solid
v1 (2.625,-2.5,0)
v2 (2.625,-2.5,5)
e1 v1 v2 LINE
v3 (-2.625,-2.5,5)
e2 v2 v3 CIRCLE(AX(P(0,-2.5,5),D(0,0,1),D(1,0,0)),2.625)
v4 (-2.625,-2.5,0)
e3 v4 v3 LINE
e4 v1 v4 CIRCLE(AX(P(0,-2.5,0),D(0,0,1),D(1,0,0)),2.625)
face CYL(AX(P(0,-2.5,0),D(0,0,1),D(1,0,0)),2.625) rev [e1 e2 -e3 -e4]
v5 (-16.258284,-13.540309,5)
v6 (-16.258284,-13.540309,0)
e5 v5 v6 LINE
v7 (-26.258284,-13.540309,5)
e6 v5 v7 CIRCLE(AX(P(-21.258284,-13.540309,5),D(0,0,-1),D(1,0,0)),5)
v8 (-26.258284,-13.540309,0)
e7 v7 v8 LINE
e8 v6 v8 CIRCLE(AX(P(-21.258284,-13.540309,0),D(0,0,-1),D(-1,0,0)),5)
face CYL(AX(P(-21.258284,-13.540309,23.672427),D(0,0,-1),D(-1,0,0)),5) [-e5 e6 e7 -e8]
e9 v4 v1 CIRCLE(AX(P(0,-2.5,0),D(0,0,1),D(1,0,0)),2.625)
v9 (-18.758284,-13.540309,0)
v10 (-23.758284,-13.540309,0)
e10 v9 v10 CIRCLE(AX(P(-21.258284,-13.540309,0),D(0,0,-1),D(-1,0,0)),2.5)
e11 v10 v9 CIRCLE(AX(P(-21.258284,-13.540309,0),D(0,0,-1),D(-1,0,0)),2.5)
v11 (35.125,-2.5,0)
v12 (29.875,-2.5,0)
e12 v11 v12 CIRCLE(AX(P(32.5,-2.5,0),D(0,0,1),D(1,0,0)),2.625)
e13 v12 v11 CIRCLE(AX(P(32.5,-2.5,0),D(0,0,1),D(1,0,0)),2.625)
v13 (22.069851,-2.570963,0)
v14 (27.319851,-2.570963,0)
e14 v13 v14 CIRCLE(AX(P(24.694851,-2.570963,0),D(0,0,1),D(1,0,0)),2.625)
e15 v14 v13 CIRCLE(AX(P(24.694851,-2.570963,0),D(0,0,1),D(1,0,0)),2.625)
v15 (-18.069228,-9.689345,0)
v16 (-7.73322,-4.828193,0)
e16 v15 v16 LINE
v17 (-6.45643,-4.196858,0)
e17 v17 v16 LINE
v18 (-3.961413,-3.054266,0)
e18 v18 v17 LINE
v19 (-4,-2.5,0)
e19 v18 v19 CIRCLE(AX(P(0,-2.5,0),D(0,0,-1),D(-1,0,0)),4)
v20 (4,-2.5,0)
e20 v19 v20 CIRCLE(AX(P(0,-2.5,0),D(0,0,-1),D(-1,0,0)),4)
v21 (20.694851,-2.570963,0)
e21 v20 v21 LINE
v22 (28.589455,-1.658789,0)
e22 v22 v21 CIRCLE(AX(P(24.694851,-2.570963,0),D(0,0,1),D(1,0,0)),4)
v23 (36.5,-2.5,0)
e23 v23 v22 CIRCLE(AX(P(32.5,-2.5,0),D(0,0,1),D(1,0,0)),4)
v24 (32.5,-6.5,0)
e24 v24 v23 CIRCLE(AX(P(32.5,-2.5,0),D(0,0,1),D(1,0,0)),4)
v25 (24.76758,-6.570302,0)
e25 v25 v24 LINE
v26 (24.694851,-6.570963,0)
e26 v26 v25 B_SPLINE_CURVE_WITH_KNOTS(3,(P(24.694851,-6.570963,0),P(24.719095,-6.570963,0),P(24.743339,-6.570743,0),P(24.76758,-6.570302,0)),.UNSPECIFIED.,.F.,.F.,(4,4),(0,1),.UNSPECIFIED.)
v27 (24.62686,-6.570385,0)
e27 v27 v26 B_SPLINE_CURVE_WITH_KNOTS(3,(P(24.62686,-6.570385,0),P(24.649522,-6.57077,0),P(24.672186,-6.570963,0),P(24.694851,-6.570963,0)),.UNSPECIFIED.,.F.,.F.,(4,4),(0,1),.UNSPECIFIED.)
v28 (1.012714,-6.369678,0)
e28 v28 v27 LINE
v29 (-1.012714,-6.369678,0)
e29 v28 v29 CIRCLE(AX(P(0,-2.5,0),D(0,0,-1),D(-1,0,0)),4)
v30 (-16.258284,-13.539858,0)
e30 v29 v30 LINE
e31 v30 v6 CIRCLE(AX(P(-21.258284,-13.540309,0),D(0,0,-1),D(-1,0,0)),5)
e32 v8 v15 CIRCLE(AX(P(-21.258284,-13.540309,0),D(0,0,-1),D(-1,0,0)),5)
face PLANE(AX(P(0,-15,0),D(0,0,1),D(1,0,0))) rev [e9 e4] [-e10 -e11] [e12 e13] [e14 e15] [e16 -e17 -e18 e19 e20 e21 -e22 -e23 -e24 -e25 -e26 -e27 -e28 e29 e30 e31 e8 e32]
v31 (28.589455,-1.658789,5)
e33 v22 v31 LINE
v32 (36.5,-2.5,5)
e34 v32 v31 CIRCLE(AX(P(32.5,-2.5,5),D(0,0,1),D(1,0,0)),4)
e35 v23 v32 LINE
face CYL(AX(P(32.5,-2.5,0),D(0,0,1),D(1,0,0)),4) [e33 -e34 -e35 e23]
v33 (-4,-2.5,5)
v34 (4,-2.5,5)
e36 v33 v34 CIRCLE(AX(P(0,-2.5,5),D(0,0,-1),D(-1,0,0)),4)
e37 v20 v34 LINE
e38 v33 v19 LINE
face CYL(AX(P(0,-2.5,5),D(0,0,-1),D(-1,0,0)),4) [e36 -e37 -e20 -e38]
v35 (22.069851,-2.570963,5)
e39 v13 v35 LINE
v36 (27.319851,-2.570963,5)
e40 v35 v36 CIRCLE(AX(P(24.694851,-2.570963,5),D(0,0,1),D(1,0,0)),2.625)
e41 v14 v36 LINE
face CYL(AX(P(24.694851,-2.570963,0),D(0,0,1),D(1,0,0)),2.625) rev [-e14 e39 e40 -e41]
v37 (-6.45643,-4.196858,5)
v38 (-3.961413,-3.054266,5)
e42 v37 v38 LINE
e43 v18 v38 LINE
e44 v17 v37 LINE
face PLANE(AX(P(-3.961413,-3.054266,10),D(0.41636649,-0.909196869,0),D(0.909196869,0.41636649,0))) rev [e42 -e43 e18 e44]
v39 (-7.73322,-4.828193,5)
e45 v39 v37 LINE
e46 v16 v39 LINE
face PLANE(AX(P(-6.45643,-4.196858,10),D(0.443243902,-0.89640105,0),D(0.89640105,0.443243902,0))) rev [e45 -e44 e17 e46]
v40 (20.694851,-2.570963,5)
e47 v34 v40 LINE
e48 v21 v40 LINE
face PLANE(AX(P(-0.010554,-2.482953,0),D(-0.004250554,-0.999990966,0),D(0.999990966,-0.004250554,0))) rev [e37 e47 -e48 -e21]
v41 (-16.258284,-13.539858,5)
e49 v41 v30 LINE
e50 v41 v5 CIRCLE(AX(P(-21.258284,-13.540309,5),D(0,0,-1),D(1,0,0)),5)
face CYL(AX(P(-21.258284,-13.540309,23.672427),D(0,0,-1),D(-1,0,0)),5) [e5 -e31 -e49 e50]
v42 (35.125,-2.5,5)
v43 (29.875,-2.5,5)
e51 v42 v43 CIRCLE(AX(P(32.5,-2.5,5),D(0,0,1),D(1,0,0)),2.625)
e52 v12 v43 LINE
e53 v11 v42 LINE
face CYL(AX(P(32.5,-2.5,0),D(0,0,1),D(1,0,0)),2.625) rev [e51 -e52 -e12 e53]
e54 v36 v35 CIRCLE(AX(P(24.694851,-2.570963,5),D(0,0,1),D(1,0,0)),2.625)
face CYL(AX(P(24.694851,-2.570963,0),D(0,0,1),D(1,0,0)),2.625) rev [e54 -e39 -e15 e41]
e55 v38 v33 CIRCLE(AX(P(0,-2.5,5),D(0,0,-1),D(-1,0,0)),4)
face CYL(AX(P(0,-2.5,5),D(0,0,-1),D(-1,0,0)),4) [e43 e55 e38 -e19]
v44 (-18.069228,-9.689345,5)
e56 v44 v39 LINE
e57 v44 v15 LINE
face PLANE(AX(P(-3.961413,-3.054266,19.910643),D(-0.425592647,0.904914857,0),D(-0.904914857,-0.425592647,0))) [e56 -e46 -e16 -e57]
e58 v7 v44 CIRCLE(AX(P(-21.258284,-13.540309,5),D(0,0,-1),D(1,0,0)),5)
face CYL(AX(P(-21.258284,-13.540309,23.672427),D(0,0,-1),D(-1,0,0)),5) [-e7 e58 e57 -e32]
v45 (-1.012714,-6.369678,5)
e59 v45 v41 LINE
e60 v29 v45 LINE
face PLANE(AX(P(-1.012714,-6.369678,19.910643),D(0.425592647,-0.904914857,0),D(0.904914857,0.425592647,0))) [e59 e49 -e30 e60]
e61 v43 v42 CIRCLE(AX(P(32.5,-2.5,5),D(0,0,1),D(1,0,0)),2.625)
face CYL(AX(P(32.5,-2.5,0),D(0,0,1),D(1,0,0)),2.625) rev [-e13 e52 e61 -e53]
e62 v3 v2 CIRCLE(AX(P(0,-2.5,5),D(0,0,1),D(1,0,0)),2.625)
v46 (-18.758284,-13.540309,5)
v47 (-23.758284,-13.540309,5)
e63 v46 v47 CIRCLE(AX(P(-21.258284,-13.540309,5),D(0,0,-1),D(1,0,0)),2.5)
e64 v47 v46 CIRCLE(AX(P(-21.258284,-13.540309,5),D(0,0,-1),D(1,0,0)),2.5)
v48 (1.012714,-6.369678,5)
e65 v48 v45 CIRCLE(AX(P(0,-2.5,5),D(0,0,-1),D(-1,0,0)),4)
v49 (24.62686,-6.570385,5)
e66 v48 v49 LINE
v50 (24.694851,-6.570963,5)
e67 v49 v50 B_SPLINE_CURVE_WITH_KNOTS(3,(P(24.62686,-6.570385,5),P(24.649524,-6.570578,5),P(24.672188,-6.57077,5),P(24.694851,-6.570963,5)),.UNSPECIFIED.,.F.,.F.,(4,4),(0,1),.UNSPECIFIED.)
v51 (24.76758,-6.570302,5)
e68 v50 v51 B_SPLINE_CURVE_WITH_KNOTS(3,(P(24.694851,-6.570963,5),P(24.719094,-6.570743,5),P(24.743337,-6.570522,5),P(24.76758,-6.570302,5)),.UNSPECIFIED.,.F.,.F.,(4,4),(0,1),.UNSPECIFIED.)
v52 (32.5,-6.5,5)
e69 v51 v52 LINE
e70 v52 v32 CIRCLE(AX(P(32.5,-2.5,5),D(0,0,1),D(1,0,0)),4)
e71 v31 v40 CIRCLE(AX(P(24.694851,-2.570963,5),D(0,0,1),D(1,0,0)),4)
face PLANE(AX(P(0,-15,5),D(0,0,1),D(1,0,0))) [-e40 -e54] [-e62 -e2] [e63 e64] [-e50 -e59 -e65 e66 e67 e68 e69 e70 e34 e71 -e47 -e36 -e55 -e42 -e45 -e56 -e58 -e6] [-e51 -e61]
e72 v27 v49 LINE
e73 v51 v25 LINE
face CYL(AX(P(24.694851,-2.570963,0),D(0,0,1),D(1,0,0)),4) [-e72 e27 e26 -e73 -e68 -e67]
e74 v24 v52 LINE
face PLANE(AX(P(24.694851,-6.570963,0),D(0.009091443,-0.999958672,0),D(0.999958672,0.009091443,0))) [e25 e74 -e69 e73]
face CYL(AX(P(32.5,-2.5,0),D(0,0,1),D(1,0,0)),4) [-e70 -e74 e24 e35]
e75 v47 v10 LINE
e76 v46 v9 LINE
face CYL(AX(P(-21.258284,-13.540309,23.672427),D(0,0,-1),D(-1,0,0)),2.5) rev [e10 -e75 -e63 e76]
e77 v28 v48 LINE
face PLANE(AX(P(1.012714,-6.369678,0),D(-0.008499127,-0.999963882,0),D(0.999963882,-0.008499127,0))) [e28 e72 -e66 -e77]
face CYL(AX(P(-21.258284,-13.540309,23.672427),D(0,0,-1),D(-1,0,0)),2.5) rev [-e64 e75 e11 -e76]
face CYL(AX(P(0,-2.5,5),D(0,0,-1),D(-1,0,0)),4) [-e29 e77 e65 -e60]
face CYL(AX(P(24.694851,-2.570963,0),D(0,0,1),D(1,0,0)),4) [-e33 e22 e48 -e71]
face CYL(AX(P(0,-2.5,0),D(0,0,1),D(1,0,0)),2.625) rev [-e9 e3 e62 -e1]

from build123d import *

# Parameters (mm, degrees)
BOSS_EXTRUDE1_DEPTH  = 5
SKETCH3_R            = 2.5
CUT_EXTRUDE3_DEPTH   = 10
SKETCH2_R            = 1.5
CUT_EXTRUDE4_DEPTH   = 7
SKETCH5_R            = 4
BOSS_EXTRUDE2_DEPTH  = 5
SKETCH6_R            = 4
BOSS_EXTRUDE3_DEPTH  = 5
BOSS_EXTRUDE4_DEPTH  = 5
SKETCH9_R            = 4
BOSS_EXTRUDE5_DEPTH  = 5
SKETCH10_R           = 2.625
SKETCH10_R_2         = 2.5
CUT_EXTRUDE5_DEPTH   = 39.359537556
SKETCH11_R           = 4
BOSS_EXTRUDE6_DEPTH  = 5
SKETCH12_R           = 2.625
CUT_EXTRUDE6_DEPTH   = 39.359537556
SKETCH13_R           = 4
BOSS_EXTRUDE7_DEPTH  = 5
CUT_EXTRUDE7_DEPTH   = 39.359537556
CUT_EXTRUDE8_DEPTH   = 39.359537556
BOSS_EXTRUDE8_DEPTH  = 5
BOSS_EXTRUDE9_DEPTH  = 5
CUT_EXTRUDE9_DEPTH   = 10
CUT_EXTRUDE10_DEPTH  = 10
CUT_EXTRUDE11_DEPTH  = 10
CUT_EXTRUDE12_DEPTH  = 10
SKETCH30_R           = 2.5
BOSS_EXTRUDE16_DEPTH = 5


with BuildPart() as part:
    # Sketch1 → Boss-Extrude1 (new body)
    with BuildSketch(Plane.XY):
        with BuildLine():
            Line((0, 0), (34, 0))
            ThreePointArc((34, 0), (34.707106781, -0.292893219), (35, -1))
            Line((35, -1), (35, -4))
            ThreePointArc((35, -4), (34.707106781, -4.707106781), (34, -5))
            Line((34, -5), (0, -5))
            ThreePointArc((0, -5), (-4.600765263, -6.121207346), (-8.169848164, -9.233408201))
            ThreePointArc((-8.169848164, -9.233408201), (-8.772233245, -9.633451101), (-9.486832981, -9.522774425))
            Line((-9.486832981, -9.522774425), (-12.093386622, -8.017879978))
            ThreePointArc((-12.093386622, -8.017879978), (-12.567944885, -7.375988891), (-12.421485667, -6.591272758))
            ThreePointArc((-12.421485667, -6.591272758), (-7.030970465, -1.749888517), (0, 0))
        make_face()
    extrude(amount=BOSS_EXTRUDE1_DEPTH)

    # Sketch3 → Cut-Extrude3 (cut)
    with BuildSketch(Plane(origin=(0, 0, 0), x_dir=(-1, 0, 0), z_dir=(0, 0, -1))):
        with Locations((0, -2.5)):
            Circle(SKETCH3_R)
    extrude(amount=-CUT_EXTRUDE3_DEPTH, mode=Mode.SUBTRACT)


with BuildPart() as cut_extrude3_piece_1:
    # of the separate pieces the step leaves, piece 1, a body of its own (cut_extrude3_pieces)
    add(part.part.solids().sort_by_distance((34, 0, 0))[0])



with BuildPart() as cut_extrude3_piece_2:
    # of the separate pieces the step leaves, piece 2, a body of its own (cut_extrude3_pieces)
    add(part.part.solids().sort_by_distance((-12.421485667, -6.591272758, 0))[0])

    # Sketch2 → Cut-Extrude4 (cut)
    with BuildSketch(Plane.XY.offset(5)):
        with Locations((32.633829537, -2.570962999)):
            Circle(SKETCH2_R)
        with Locations((-9.587088302, -6.686632842)):
            Circle(SKETCH2_R)
        with Locations((24.694851026, -2.570962999)):
            Circle(SKETCH2_R)
    extrude(amount=-CUT_EXTRUDE4_DEPTH, mode=Mode.SUBTRACT)


with BuildPart() as cut_extrude3_piece_1_1:
    add(cut_extrude3_piece_1.part)

    add(cut_extrude3_piece_2.part)  # Boss-Extrude2 merges Cut-Extrude3 piece 2
    # Sketch5 → Boss-Extrude2 (add)
    with BuildSketch(Plane(origin=(0, 0, 0), x_dir=(-1, 0, 0), z_dir=(0, 0, -1))):
        with Locations((0, -2.5)):
            Circle(SKETCH5_R)
    extrude(amount=-BOSS_EXTRUDE2_DEPTH)

    # Sketch6 → Boss-Extrude3 (add, through all)
    with BuildSketch(Plane.XY.offset(5)):
        with Locations((16.69060283, -2.5)):
            Circle(SKETCH6_R)
    extrude(amount=-BOSS_EXTRUDE3_DEPTH)

    # Sketch7 → Boss-Extrude4 (add, through all)
    with BuildSketch(Plane.XY.offset(5)):
        with BuildLine():
            ThreePointArc((29.377501001, -5), (33.824764885, -6.274254628), (36.5, -2.5))
            ThreePointArc((36.5, -2.5), (33.824764885, 1.274254628), (29.377501001, 0))
            Line((29.377501001, 0), (34, 0))
            ThreePointArc((34, 0), (34.707106781, -0.292893219), (35, -1))
            Line((35, -1), (35, -2.5))
            Line((35, -2.5), (35, -4))
            ThreePointArc((35, -4), (34.707106781, -4.707106781), (34, -5))
            Line((34, -5), (29.377501001, -5))
        make_face()
    extrude(amount=-BOSS_EXTRUDE4_DEPTH)

    # Sketch9 → Boss-Extrude5 (add, through all)
    with BuildSketch(Plane.XY.offset(5)):
        with Locations((-9.587088302, -6.686632842)):
            Circle(SKETCH9_R)
    extrude(amount=-BOSS_EXTRUDE5_DEPTH)

    # Sketch10 → Cut-Extrude5 (cut, through all)
    with BuildSketch(Plane.XY.offset(5)):
        with Locations((0, -2.5)):
            Circle(SKETCH10_R)
        with Locations((-9.587088302, -6.686632842)):
            Circle(SKETCH10_R)
        with Locations((16.69060283, -2.5)):
            Circle(SKETCH10_R_2)
        with Locations((32.5, -2.5)):
            Circle(SKETCH10_R)
    extrude(amount=-CUT_EXTRUDE5_DEPTH, mode=Mode.SUBTRACT)

    # Sketch11 → Boss-Extrude6 (add, through all)
    with BuildSketch(Plane.XY.offset(5)):
        with Locations((24.694851026, -2.570962999)):
            Circle(SKETCH11_R)
    extrude(amount=-BOSS_EXTRUDE6_DEPTH)

    # Sketch12 → Cut-Extrude6 (cut, through all)
    with BuildSketch(Plane.XY.offset(5)):
        with Locations((24.694851026, -2.570962999)):
            Circle(SKETCH12_R)
    extrude(amount=-CUT_EXTRUDE6_DEPTH, mode=Mode.SUBTRACT)

    # Sketch13 → Boss-Extrude7 (add, through all)
    with BuildSketch(Plane.XY.offset(5)):
        with Locations((16.69060283, -2.5)):
            Circle(SKETCH13_R)
    extrude(amount=-BOSS_EXTRUDE7_DEPTH)

    # Sketch14 → Cut-Extrude7 (cut, through all)
    with BuildSketch(Plane.XY.offset(5)):
        Polygon((13.568103831, 0), (19.813101829, 0), (19.608152419, 3.101401215), (13.568103831, 2.844182656), (12.582024398, 1.287333479), align=None)
        Polygon((13.568103831, -5), (19.813101829, -5), (20.934648885, -7.644859521), (15.442425287, -9.366014099), (11.632678636, -7.644859521), align=None)
    extrude(amount=-CUT_EXTRUDE7_DEPTH, mode=Mode.SUBTRACT)

    # Sketch15 → Cut-Extrude8 (cut, through all)
    with BuildSketch(Plane.XY.offset(5)):
        Polygon((21.630515983, 0), (5.499420419, 2.191296742), (3.122498999, 0), align=None)
        with BuildLine():
            ThreePointArc((21.630515983, 0), (20.936038702, -1.202997388), (20.694851026, -2.570962999))
            Line((20.694851026, -2.570962999), (4, -2.5))
            ThreePointArc((4, -2.5), (3.774254628, -1.175235115), (3.122498999, 0))
            Line((3.122498999, 0), (21.630515983, 0))
        make_face()
        with BuildLine():
            Line((-7.607535591, 0.794757928), (-3.398220122, -0.39))
            ThreePointArc((-3.398220122, -0.39), (-6.16935857, -1.327435689), (-8.705842203, -2.784914591))
            Line((-8.705842203, -2.784914591), (-7.607535591, 0.794757928))
        make_face()
        with BuildLine():
            ThreePointArc((-3.398220122, -0.39), (-6.16935857, -1.327435689), (-8.705842203, -2.784914591))
            ThreePointArc((-8.705842203, -2.784914591), (-7.460532252, -3.29874864), (-6.456429886, -4.196858178))
            ThreePointArc((-6.456429886, -4.196858178), (-5.240156475, -3.557355191), (-3.961412583, -3.054265596))
            ThreePointArc((-3.961412583, -3.054265596), (-3.913518389, -1.672731107), (-3.398220122, -0.39))
        make_face()
        Polygon((28.45366335, 2.528160998), (29.377501001, 0), (27.75918607, 0), align=None)
        with BuildLine():
            Line((29.377501001, 0), (27.75918607, 0))
            ThreePointArc((27.75918607, 0), (28.271805382, -0.780600595), (28.589454783, -1.658788905))
            ThreePointArc((28.589454783, -1.658788905), (28.886992542, -0.783556844), (29.377501001, 0))
        make_face()
    extrude(amount=-CUT_EXTRUDE8_DEPTH, mode=Mode.SUBTRACT)

    # Sketch16 → Boss-Extrude8 (add, through all)
    with BuildSketch(Plane.XY.offset(5)):
        with BuildLine():
            Line((1.01271432, -6.369678243), (24.694851026, -6.570962999))
            Line((24.694851026, -6.570962999), (32.5, -6.5))
            Line((32.5, -6.5), (28.834380203, -3.557484395))
            Line((28.834380203, -3.557484395), (25.878705121, -5.379005085))
            Line((25.878705121, -5.379005085), (23.335449819, -5.379005085))
            Line((23.335449819, -5.379005085), (21.307719239, -4.244850693))
            Line((21.307719239, -4.244850693), (3.023775712, -3.866799229))
            Line((3.023775712, -3.866799229), (0.570007719, -5.379005085))
            Line((0.570007719, -5.379005085), (-2.853206137, -4.622902157))
            Line((-2.853206137, -4.622902157), (-6.221300997, -5.963266438))
            Line((-6.221300997, -5.963266438), (-6.565043066, -9.307175266))
            ThreePointArc((-6.565043066, -9.307175266), (-3.14075004, -6.897917977), (1.01271432, -6.369678243))
        make_face()
    extrude(amount=-BOSS_EXTRUDE8_DEPTH)

    # Sketch17 → Boss-Extrude9 (add)
    with BuildSketch(Plane(origin=(0, 0, 0), x_dir=(-1, 0, 0), z_dir=(0, 0, -1))):
        Polygon((3.961412583, -3.054265596), (13.495388719, -7.538212462), (11.30366334, -11.209638817), (1.01271432, -6.369678243), align=None)
    extrude(amount=-BOSS_EXTRUDE9_DEPTH)

    # Sketch18 → Cut-Extrude9 (cut)
    with BuildSketch(Plane(origin=(0, 0, 0), x_dir=(-1, 0, 0), z_dir=(0, 0, -1))):
        with BuildLine():
            Line((3.961412583, -3.054265596), (6.456429886, -4.196858178))
            ThreePointArc((6.456429886, -4.196858178), (5.240156475, -3.557355191), (3.961412583, -3.054265596))
        make_face()
    extrude(amount=-CUT_EXTRUDE9_DEPTH, mode=Mode.SUBTRACT)

    # Sketch19 → Cut-Extrude10 (cut)
    with BuildSketch(Plane(origin=(0, 0, 0), x_dir=(-1, 0, 0), z_dir=(0, 0, -1))):
        with BuildLine():
            Line((6.001656968, -8.71603966), (10.116735554, -10.651412003))
            ThreePointArc((10.116735554, -10.651412003), (7.658367525, -10.535986511), (6.001656968, -8.71603966))
        make_face()
    extrude(amount=-CUT_EXTRUDE10_DEPTH, mode=Mode.SUBTRACT)

    # Sketch20 → Cut-Extrude11 (cut)
    with BuildSketch(Plane(origin=(0, 0, 0), x_dir=(-1, 0, 0), z_dir=(0, 0, -1))):
        Polygon((6.456429886, -4.196858178), (7.733220064, -4.828193293), (12.200841034, -6.929370679), (14.105694097, -7.825246628), (14.33213787, -2.397708334), (7.630569976, -1.451472026), align=None)
    extrude(amount=-CUT_EXTRUDE11_DEPTH, mode=Mode.SUBTRACT)

    # Sketch21 → Cut-Extrude12 (cut)
    with BuildSketch(Plane(origin=(0, 0, 0), x_dir=(-1, 0, 0), z_dir=(0, 0, -1))):
        Polygon((11.30366334, -11.209638817), (13.114607064, -7.359126141), (14.222505477, -7.880184465), (12.35401945, -11.85304626), align=None)
    extrude(amount=-CUT_EXTRUDE12_DEPTH, mode=Mode.SUBTRACT)

    # Sketch30 → Boss-Extrude16 (add)
    with BuildSketch(Plane(origin=(0, 0, 0), x_dir=(-1, 0, 0), z_dir=(0, 0, -1))):
        with BuildLine():
            Line((13.114607064, -7.359126141), (11.30366334, -11.209638817))
            Line((11.30366334, -11.209638817), (16.258283795, -13.539858082))
            ThreePointArc((16.258283795, -13.539858082), (25.782858061, -15.668272182), (18.069227519, -9.689345407))
            Line((18.069227519, -9.689345407), (13.114607064, -7.359126141))
        make_face()
        with Locations((21.258283775, -13.540308948)):
            Circle(SKETCH30_R, mode=Mode.SUBTRACT)
    extrude(amount=-BOSS_EXTRUDE16_DEPTH)


solid = cut_extrude3_piece_1_1.part
